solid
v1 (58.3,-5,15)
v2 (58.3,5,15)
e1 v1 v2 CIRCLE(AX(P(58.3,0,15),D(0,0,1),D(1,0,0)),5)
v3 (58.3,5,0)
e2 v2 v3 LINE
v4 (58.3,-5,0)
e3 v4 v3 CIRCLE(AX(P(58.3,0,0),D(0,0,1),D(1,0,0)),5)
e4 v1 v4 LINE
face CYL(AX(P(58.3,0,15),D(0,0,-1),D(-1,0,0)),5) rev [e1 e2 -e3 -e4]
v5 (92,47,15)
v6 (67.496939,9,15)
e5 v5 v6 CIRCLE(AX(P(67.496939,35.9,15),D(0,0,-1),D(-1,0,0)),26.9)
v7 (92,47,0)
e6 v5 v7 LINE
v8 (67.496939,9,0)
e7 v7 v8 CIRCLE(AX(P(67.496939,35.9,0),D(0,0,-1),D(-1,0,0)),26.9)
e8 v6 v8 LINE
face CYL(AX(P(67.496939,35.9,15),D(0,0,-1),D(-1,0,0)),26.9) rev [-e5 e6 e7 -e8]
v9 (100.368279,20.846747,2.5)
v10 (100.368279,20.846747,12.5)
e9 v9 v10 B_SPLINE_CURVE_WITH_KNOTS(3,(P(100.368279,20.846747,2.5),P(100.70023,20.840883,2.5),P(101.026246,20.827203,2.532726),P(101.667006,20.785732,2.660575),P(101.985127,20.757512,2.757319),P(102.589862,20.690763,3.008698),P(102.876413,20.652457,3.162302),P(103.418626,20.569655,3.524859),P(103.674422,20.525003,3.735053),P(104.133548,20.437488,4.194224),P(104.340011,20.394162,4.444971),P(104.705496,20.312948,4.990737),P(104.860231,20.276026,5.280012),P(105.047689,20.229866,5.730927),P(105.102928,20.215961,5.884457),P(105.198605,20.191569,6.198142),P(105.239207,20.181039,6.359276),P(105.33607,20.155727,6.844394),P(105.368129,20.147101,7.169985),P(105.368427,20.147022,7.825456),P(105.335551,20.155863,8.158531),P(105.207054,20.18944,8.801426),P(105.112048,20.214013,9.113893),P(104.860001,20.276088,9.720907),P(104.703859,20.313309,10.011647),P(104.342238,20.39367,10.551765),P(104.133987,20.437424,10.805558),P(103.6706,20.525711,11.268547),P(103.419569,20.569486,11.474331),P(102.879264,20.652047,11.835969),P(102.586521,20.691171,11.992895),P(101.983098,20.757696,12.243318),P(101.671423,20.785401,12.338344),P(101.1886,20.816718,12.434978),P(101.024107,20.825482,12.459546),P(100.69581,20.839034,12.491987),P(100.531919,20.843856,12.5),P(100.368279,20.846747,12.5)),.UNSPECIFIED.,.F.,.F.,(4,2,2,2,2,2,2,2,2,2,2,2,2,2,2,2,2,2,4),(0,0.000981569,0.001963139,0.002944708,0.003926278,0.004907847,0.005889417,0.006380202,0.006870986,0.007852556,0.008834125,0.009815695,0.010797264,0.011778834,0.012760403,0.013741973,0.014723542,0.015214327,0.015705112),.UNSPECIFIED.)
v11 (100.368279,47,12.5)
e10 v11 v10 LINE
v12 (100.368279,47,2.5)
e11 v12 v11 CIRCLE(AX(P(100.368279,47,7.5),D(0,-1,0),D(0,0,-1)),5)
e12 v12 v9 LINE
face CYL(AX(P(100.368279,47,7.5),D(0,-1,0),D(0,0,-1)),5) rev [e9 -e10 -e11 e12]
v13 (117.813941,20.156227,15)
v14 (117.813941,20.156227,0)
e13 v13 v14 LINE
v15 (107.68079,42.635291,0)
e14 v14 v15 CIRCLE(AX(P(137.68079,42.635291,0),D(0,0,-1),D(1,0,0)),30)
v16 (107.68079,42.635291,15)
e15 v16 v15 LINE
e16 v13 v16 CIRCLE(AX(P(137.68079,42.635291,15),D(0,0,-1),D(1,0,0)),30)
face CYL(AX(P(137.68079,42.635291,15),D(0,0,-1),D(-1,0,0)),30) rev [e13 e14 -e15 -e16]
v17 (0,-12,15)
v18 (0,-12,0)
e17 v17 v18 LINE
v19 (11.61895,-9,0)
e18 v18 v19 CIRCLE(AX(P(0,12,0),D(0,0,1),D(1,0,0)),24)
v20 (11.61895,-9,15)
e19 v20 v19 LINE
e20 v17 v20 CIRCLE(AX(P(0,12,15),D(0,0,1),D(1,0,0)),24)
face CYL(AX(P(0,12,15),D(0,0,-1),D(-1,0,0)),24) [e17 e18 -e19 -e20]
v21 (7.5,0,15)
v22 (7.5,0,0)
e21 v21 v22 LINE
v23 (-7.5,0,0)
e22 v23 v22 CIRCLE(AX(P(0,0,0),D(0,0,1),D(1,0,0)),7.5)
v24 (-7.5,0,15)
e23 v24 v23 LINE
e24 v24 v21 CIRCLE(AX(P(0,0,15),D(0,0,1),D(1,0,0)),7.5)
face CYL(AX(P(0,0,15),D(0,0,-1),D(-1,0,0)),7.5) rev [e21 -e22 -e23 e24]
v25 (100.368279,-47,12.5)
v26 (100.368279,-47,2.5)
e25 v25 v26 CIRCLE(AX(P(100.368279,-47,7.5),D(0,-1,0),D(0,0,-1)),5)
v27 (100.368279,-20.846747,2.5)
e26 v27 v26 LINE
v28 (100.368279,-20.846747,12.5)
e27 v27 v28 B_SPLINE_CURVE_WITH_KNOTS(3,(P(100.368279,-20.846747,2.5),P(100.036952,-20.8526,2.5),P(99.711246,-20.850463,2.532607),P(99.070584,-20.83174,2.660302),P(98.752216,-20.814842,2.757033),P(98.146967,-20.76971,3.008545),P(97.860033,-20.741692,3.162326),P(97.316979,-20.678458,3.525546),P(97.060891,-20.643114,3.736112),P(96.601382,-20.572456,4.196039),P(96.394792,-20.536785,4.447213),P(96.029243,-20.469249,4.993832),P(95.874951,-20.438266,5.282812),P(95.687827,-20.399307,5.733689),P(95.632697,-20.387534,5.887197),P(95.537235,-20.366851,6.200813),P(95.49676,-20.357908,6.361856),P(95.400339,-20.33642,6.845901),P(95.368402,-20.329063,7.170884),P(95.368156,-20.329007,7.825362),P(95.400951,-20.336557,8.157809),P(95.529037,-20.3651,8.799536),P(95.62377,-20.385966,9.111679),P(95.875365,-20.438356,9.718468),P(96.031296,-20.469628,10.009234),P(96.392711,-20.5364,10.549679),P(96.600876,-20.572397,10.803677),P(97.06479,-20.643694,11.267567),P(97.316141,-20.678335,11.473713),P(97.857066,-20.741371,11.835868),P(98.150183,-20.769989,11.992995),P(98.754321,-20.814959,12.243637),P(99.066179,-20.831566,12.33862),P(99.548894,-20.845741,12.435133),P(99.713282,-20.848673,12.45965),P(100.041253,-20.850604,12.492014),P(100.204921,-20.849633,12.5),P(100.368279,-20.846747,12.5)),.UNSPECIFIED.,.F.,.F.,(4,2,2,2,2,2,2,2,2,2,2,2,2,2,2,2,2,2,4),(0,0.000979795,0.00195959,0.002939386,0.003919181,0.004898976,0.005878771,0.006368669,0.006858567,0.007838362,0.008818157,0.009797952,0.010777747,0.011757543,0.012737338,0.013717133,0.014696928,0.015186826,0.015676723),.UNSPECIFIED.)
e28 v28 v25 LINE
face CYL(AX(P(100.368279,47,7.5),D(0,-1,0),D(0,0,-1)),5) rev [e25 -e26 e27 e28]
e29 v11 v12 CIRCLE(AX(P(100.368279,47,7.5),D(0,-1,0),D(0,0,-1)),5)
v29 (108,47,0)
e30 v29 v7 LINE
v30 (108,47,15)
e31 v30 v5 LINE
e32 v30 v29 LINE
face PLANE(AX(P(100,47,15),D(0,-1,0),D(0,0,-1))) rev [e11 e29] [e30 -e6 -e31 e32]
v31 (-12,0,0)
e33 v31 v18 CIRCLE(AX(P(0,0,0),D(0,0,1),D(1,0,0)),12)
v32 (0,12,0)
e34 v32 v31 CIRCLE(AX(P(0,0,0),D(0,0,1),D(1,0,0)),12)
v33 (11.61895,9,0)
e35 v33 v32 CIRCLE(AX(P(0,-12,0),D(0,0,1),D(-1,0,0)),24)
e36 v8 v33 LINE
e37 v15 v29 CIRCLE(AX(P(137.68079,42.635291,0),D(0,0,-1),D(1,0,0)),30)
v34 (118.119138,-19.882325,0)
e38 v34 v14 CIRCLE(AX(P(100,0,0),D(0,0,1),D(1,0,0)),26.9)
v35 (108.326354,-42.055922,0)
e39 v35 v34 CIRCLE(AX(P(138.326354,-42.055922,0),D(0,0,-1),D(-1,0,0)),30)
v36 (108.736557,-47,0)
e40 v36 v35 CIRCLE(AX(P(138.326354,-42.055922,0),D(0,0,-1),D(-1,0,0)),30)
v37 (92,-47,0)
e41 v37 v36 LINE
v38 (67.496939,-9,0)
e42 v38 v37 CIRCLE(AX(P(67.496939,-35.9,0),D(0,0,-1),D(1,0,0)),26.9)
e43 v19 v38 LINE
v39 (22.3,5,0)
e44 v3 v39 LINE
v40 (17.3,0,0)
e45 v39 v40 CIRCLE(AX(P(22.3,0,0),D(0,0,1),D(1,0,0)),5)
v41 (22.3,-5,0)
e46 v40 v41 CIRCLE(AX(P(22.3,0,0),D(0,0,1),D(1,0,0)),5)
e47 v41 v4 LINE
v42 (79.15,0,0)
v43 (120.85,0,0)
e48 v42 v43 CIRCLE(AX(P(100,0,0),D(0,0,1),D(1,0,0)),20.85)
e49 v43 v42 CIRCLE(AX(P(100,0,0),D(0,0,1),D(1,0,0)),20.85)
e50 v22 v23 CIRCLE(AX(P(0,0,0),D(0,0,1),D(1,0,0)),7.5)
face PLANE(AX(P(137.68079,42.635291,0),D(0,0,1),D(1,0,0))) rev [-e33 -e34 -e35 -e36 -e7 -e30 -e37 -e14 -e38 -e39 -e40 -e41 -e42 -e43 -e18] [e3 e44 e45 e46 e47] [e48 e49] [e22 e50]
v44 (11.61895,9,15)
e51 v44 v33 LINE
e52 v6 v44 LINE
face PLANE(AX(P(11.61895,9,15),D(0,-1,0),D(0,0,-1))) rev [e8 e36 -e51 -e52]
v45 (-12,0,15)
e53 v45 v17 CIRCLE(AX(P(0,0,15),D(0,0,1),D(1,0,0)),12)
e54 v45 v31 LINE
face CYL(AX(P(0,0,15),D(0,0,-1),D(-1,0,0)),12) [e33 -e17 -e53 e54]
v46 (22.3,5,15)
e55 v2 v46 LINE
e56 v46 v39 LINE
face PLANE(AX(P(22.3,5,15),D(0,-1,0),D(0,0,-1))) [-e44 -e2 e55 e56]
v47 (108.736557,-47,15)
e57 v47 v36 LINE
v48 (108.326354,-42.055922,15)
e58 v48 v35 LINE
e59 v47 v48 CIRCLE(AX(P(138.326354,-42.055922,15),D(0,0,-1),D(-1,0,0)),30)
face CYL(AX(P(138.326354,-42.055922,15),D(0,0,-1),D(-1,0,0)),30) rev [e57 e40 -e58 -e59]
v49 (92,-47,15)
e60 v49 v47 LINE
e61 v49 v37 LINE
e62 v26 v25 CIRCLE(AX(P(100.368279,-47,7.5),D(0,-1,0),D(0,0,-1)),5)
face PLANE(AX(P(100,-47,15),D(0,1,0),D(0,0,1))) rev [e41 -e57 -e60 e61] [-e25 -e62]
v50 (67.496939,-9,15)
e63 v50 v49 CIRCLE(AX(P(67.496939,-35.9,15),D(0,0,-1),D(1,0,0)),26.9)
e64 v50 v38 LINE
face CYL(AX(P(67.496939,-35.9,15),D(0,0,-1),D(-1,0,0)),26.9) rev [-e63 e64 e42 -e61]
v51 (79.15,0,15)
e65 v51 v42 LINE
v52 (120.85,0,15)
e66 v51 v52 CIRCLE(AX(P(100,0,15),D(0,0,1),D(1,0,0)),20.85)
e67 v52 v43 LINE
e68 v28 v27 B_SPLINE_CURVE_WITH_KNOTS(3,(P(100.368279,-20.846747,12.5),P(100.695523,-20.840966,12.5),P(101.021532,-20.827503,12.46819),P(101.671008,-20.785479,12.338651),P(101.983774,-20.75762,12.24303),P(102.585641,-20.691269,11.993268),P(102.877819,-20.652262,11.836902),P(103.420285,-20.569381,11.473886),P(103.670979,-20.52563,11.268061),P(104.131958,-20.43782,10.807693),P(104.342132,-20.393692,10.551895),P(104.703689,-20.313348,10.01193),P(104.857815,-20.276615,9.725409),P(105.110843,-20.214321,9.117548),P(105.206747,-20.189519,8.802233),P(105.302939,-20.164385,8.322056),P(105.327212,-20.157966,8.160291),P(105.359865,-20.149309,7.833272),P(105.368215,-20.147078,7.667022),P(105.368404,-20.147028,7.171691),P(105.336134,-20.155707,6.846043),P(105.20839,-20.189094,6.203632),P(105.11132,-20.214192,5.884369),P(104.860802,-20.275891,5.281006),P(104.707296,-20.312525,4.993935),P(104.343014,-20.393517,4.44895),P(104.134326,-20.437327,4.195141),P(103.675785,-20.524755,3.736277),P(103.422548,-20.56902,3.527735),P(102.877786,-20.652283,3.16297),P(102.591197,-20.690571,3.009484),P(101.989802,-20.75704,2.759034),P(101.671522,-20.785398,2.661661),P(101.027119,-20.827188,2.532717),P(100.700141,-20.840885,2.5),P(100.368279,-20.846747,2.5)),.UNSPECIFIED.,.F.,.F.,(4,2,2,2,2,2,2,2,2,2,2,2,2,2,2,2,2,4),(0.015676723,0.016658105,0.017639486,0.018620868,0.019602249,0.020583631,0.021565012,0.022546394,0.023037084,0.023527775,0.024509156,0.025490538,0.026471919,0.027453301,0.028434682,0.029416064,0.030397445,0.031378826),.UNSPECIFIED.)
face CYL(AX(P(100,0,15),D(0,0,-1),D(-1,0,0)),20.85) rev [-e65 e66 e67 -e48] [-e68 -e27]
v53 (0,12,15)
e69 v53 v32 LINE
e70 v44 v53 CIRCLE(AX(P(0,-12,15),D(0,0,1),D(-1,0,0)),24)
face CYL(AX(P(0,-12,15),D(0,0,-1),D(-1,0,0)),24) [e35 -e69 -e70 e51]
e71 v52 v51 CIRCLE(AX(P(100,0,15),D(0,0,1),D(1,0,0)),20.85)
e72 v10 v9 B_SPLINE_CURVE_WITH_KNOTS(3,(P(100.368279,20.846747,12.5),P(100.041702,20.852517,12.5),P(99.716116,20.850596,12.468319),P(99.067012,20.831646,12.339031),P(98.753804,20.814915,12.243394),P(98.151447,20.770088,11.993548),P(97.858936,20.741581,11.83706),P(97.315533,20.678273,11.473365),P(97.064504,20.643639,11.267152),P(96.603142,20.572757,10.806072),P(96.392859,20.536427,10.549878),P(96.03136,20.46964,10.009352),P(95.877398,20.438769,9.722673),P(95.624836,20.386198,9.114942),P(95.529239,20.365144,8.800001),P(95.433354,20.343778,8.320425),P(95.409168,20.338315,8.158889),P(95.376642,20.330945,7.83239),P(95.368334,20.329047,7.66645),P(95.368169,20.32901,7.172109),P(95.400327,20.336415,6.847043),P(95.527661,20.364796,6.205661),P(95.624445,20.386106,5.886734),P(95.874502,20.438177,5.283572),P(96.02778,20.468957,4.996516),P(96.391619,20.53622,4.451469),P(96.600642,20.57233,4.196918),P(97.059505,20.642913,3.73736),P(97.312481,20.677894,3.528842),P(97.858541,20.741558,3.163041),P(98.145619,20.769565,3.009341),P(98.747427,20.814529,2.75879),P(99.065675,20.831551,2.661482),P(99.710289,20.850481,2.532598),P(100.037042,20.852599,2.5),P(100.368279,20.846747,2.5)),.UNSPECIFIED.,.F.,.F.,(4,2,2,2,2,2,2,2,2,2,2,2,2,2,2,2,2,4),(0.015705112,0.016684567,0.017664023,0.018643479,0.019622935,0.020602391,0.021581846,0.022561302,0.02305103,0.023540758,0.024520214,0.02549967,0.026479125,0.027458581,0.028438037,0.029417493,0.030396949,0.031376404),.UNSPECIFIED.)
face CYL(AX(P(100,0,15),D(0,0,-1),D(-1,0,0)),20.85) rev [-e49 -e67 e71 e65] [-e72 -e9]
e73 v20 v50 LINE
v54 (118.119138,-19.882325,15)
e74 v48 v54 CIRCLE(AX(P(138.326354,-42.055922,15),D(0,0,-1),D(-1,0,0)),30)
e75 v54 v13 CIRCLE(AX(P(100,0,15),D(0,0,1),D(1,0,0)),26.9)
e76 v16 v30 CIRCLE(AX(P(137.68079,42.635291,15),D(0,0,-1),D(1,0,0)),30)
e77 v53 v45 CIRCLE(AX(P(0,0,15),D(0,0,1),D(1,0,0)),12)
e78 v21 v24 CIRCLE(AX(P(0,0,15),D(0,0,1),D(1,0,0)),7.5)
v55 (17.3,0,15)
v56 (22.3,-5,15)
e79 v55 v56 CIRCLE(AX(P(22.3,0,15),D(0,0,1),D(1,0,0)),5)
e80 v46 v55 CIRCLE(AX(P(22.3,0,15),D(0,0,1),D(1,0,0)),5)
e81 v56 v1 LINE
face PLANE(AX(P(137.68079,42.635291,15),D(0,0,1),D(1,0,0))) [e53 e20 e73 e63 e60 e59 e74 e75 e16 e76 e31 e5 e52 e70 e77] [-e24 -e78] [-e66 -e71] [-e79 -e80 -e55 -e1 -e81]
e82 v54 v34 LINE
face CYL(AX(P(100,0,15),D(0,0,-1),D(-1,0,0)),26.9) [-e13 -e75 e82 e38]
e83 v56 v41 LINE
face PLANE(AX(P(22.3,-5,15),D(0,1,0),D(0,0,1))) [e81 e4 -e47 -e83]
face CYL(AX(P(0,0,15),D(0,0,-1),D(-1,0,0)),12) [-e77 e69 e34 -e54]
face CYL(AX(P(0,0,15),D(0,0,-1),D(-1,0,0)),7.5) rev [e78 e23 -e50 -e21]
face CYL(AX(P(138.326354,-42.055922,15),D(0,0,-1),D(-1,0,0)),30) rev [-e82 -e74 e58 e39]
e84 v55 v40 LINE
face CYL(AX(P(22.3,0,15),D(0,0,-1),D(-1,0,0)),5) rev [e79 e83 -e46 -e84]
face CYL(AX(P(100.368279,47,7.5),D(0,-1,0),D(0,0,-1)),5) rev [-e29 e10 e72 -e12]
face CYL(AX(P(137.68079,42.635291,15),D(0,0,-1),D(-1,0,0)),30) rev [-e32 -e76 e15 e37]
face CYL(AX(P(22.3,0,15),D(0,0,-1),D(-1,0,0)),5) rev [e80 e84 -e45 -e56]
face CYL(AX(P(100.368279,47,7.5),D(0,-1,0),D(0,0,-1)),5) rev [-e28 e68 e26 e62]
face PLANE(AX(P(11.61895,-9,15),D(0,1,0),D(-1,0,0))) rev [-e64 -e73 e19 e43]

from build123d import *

# Parameters (mm, degrees)
LINK_PROFILE_SKETCH_R   = 7.5
LINK_PROFILE_SKETCH_R_2 = 20.85
LINK_BODY_15MM_DEPTH    = 15
BOLT_HOLE_SKETCH_R      = 5
BOLT_HOLE_10_DEPTH      = 159.633571478


with BuildPart() as part:
    # Link Profile Sketch → Link Body 15mm (new body)
    with BuildSketch(Plane.XY):
        with BuildLine():
            Line((100, 47), (92, 47))
            ThreePointArc((92, 47), (90.104459839, 21.32227727), (67.496938967, 9))
            Line((67.496938967, 9), (11.618950039, 9))
            ThreePointArc((11.618950039, 9), (6, 11.237900077), (0, 12))
            ThreePointArc((0, 12), (-12, 0), (0, -12))
            ThreePointArc((0, -12), (6, -11.237900077), (11.618950039, -9))
            Line((11.618950039, -9), (67.496938967, -9))
            ThreePointArc((67.496938967, -9), (90.104459839, -21.32227727), (92, -47))
            Line((92, -47), (100, -47))
            Line((100, -47), (108.73655718, -47))
            ThreePointArc((108.73655718, -47), (109.975380436, -32.246626192), (118.119137608, -19.882325124))
            ThreePointArc((118.119137608, -19.882325124), (126.899218543, 0.205040931), (117.813941305, 20.156227206))
            ThreePointArc((117.813941305, 20.156227206), (109.504751294, 32.334280207), (108, 47))
            Line((108, 47), (100, 47))
        make_face()
        Circle(LINK_PROFILE_SKETCH_R, mode=Mode.SUBTRACT)
        with Locations((100, 0)):
            Circle(LINK_PROFILE_SKETCH_R_2, mode=Mode.SUBTRACT)
        with BuildLine():
            Line((22.3, -5), (58.3, -5))
            ThreePointArc((58.3, -5), (63.3, 0), (58.3, 5))
            Line((58.3, 5), (22.3, 5))
            ThreePointArc((22.3, 5), (17.3, 0), (22.3, -5))
        make_face(mode=Mode.SUBTRACT)
    extrude(amount=LINK_BODY_15MM_DEPTH)

    # Bolt Hole Sketch → Bolt Hole Ø10 (cut, through all)
    with BuildSketch(Plane.XZ.offset(47)):
        with Locations(Location((100.36827859, 7.5, 0), (0, 0, 270))):
            Circle(BOLT_HOLE_SKETCH_R)
    extrude(amount=-BOLT_HOLE_10_DEPTH, mode=Mode.SUBTRACT)


solid = part.part
